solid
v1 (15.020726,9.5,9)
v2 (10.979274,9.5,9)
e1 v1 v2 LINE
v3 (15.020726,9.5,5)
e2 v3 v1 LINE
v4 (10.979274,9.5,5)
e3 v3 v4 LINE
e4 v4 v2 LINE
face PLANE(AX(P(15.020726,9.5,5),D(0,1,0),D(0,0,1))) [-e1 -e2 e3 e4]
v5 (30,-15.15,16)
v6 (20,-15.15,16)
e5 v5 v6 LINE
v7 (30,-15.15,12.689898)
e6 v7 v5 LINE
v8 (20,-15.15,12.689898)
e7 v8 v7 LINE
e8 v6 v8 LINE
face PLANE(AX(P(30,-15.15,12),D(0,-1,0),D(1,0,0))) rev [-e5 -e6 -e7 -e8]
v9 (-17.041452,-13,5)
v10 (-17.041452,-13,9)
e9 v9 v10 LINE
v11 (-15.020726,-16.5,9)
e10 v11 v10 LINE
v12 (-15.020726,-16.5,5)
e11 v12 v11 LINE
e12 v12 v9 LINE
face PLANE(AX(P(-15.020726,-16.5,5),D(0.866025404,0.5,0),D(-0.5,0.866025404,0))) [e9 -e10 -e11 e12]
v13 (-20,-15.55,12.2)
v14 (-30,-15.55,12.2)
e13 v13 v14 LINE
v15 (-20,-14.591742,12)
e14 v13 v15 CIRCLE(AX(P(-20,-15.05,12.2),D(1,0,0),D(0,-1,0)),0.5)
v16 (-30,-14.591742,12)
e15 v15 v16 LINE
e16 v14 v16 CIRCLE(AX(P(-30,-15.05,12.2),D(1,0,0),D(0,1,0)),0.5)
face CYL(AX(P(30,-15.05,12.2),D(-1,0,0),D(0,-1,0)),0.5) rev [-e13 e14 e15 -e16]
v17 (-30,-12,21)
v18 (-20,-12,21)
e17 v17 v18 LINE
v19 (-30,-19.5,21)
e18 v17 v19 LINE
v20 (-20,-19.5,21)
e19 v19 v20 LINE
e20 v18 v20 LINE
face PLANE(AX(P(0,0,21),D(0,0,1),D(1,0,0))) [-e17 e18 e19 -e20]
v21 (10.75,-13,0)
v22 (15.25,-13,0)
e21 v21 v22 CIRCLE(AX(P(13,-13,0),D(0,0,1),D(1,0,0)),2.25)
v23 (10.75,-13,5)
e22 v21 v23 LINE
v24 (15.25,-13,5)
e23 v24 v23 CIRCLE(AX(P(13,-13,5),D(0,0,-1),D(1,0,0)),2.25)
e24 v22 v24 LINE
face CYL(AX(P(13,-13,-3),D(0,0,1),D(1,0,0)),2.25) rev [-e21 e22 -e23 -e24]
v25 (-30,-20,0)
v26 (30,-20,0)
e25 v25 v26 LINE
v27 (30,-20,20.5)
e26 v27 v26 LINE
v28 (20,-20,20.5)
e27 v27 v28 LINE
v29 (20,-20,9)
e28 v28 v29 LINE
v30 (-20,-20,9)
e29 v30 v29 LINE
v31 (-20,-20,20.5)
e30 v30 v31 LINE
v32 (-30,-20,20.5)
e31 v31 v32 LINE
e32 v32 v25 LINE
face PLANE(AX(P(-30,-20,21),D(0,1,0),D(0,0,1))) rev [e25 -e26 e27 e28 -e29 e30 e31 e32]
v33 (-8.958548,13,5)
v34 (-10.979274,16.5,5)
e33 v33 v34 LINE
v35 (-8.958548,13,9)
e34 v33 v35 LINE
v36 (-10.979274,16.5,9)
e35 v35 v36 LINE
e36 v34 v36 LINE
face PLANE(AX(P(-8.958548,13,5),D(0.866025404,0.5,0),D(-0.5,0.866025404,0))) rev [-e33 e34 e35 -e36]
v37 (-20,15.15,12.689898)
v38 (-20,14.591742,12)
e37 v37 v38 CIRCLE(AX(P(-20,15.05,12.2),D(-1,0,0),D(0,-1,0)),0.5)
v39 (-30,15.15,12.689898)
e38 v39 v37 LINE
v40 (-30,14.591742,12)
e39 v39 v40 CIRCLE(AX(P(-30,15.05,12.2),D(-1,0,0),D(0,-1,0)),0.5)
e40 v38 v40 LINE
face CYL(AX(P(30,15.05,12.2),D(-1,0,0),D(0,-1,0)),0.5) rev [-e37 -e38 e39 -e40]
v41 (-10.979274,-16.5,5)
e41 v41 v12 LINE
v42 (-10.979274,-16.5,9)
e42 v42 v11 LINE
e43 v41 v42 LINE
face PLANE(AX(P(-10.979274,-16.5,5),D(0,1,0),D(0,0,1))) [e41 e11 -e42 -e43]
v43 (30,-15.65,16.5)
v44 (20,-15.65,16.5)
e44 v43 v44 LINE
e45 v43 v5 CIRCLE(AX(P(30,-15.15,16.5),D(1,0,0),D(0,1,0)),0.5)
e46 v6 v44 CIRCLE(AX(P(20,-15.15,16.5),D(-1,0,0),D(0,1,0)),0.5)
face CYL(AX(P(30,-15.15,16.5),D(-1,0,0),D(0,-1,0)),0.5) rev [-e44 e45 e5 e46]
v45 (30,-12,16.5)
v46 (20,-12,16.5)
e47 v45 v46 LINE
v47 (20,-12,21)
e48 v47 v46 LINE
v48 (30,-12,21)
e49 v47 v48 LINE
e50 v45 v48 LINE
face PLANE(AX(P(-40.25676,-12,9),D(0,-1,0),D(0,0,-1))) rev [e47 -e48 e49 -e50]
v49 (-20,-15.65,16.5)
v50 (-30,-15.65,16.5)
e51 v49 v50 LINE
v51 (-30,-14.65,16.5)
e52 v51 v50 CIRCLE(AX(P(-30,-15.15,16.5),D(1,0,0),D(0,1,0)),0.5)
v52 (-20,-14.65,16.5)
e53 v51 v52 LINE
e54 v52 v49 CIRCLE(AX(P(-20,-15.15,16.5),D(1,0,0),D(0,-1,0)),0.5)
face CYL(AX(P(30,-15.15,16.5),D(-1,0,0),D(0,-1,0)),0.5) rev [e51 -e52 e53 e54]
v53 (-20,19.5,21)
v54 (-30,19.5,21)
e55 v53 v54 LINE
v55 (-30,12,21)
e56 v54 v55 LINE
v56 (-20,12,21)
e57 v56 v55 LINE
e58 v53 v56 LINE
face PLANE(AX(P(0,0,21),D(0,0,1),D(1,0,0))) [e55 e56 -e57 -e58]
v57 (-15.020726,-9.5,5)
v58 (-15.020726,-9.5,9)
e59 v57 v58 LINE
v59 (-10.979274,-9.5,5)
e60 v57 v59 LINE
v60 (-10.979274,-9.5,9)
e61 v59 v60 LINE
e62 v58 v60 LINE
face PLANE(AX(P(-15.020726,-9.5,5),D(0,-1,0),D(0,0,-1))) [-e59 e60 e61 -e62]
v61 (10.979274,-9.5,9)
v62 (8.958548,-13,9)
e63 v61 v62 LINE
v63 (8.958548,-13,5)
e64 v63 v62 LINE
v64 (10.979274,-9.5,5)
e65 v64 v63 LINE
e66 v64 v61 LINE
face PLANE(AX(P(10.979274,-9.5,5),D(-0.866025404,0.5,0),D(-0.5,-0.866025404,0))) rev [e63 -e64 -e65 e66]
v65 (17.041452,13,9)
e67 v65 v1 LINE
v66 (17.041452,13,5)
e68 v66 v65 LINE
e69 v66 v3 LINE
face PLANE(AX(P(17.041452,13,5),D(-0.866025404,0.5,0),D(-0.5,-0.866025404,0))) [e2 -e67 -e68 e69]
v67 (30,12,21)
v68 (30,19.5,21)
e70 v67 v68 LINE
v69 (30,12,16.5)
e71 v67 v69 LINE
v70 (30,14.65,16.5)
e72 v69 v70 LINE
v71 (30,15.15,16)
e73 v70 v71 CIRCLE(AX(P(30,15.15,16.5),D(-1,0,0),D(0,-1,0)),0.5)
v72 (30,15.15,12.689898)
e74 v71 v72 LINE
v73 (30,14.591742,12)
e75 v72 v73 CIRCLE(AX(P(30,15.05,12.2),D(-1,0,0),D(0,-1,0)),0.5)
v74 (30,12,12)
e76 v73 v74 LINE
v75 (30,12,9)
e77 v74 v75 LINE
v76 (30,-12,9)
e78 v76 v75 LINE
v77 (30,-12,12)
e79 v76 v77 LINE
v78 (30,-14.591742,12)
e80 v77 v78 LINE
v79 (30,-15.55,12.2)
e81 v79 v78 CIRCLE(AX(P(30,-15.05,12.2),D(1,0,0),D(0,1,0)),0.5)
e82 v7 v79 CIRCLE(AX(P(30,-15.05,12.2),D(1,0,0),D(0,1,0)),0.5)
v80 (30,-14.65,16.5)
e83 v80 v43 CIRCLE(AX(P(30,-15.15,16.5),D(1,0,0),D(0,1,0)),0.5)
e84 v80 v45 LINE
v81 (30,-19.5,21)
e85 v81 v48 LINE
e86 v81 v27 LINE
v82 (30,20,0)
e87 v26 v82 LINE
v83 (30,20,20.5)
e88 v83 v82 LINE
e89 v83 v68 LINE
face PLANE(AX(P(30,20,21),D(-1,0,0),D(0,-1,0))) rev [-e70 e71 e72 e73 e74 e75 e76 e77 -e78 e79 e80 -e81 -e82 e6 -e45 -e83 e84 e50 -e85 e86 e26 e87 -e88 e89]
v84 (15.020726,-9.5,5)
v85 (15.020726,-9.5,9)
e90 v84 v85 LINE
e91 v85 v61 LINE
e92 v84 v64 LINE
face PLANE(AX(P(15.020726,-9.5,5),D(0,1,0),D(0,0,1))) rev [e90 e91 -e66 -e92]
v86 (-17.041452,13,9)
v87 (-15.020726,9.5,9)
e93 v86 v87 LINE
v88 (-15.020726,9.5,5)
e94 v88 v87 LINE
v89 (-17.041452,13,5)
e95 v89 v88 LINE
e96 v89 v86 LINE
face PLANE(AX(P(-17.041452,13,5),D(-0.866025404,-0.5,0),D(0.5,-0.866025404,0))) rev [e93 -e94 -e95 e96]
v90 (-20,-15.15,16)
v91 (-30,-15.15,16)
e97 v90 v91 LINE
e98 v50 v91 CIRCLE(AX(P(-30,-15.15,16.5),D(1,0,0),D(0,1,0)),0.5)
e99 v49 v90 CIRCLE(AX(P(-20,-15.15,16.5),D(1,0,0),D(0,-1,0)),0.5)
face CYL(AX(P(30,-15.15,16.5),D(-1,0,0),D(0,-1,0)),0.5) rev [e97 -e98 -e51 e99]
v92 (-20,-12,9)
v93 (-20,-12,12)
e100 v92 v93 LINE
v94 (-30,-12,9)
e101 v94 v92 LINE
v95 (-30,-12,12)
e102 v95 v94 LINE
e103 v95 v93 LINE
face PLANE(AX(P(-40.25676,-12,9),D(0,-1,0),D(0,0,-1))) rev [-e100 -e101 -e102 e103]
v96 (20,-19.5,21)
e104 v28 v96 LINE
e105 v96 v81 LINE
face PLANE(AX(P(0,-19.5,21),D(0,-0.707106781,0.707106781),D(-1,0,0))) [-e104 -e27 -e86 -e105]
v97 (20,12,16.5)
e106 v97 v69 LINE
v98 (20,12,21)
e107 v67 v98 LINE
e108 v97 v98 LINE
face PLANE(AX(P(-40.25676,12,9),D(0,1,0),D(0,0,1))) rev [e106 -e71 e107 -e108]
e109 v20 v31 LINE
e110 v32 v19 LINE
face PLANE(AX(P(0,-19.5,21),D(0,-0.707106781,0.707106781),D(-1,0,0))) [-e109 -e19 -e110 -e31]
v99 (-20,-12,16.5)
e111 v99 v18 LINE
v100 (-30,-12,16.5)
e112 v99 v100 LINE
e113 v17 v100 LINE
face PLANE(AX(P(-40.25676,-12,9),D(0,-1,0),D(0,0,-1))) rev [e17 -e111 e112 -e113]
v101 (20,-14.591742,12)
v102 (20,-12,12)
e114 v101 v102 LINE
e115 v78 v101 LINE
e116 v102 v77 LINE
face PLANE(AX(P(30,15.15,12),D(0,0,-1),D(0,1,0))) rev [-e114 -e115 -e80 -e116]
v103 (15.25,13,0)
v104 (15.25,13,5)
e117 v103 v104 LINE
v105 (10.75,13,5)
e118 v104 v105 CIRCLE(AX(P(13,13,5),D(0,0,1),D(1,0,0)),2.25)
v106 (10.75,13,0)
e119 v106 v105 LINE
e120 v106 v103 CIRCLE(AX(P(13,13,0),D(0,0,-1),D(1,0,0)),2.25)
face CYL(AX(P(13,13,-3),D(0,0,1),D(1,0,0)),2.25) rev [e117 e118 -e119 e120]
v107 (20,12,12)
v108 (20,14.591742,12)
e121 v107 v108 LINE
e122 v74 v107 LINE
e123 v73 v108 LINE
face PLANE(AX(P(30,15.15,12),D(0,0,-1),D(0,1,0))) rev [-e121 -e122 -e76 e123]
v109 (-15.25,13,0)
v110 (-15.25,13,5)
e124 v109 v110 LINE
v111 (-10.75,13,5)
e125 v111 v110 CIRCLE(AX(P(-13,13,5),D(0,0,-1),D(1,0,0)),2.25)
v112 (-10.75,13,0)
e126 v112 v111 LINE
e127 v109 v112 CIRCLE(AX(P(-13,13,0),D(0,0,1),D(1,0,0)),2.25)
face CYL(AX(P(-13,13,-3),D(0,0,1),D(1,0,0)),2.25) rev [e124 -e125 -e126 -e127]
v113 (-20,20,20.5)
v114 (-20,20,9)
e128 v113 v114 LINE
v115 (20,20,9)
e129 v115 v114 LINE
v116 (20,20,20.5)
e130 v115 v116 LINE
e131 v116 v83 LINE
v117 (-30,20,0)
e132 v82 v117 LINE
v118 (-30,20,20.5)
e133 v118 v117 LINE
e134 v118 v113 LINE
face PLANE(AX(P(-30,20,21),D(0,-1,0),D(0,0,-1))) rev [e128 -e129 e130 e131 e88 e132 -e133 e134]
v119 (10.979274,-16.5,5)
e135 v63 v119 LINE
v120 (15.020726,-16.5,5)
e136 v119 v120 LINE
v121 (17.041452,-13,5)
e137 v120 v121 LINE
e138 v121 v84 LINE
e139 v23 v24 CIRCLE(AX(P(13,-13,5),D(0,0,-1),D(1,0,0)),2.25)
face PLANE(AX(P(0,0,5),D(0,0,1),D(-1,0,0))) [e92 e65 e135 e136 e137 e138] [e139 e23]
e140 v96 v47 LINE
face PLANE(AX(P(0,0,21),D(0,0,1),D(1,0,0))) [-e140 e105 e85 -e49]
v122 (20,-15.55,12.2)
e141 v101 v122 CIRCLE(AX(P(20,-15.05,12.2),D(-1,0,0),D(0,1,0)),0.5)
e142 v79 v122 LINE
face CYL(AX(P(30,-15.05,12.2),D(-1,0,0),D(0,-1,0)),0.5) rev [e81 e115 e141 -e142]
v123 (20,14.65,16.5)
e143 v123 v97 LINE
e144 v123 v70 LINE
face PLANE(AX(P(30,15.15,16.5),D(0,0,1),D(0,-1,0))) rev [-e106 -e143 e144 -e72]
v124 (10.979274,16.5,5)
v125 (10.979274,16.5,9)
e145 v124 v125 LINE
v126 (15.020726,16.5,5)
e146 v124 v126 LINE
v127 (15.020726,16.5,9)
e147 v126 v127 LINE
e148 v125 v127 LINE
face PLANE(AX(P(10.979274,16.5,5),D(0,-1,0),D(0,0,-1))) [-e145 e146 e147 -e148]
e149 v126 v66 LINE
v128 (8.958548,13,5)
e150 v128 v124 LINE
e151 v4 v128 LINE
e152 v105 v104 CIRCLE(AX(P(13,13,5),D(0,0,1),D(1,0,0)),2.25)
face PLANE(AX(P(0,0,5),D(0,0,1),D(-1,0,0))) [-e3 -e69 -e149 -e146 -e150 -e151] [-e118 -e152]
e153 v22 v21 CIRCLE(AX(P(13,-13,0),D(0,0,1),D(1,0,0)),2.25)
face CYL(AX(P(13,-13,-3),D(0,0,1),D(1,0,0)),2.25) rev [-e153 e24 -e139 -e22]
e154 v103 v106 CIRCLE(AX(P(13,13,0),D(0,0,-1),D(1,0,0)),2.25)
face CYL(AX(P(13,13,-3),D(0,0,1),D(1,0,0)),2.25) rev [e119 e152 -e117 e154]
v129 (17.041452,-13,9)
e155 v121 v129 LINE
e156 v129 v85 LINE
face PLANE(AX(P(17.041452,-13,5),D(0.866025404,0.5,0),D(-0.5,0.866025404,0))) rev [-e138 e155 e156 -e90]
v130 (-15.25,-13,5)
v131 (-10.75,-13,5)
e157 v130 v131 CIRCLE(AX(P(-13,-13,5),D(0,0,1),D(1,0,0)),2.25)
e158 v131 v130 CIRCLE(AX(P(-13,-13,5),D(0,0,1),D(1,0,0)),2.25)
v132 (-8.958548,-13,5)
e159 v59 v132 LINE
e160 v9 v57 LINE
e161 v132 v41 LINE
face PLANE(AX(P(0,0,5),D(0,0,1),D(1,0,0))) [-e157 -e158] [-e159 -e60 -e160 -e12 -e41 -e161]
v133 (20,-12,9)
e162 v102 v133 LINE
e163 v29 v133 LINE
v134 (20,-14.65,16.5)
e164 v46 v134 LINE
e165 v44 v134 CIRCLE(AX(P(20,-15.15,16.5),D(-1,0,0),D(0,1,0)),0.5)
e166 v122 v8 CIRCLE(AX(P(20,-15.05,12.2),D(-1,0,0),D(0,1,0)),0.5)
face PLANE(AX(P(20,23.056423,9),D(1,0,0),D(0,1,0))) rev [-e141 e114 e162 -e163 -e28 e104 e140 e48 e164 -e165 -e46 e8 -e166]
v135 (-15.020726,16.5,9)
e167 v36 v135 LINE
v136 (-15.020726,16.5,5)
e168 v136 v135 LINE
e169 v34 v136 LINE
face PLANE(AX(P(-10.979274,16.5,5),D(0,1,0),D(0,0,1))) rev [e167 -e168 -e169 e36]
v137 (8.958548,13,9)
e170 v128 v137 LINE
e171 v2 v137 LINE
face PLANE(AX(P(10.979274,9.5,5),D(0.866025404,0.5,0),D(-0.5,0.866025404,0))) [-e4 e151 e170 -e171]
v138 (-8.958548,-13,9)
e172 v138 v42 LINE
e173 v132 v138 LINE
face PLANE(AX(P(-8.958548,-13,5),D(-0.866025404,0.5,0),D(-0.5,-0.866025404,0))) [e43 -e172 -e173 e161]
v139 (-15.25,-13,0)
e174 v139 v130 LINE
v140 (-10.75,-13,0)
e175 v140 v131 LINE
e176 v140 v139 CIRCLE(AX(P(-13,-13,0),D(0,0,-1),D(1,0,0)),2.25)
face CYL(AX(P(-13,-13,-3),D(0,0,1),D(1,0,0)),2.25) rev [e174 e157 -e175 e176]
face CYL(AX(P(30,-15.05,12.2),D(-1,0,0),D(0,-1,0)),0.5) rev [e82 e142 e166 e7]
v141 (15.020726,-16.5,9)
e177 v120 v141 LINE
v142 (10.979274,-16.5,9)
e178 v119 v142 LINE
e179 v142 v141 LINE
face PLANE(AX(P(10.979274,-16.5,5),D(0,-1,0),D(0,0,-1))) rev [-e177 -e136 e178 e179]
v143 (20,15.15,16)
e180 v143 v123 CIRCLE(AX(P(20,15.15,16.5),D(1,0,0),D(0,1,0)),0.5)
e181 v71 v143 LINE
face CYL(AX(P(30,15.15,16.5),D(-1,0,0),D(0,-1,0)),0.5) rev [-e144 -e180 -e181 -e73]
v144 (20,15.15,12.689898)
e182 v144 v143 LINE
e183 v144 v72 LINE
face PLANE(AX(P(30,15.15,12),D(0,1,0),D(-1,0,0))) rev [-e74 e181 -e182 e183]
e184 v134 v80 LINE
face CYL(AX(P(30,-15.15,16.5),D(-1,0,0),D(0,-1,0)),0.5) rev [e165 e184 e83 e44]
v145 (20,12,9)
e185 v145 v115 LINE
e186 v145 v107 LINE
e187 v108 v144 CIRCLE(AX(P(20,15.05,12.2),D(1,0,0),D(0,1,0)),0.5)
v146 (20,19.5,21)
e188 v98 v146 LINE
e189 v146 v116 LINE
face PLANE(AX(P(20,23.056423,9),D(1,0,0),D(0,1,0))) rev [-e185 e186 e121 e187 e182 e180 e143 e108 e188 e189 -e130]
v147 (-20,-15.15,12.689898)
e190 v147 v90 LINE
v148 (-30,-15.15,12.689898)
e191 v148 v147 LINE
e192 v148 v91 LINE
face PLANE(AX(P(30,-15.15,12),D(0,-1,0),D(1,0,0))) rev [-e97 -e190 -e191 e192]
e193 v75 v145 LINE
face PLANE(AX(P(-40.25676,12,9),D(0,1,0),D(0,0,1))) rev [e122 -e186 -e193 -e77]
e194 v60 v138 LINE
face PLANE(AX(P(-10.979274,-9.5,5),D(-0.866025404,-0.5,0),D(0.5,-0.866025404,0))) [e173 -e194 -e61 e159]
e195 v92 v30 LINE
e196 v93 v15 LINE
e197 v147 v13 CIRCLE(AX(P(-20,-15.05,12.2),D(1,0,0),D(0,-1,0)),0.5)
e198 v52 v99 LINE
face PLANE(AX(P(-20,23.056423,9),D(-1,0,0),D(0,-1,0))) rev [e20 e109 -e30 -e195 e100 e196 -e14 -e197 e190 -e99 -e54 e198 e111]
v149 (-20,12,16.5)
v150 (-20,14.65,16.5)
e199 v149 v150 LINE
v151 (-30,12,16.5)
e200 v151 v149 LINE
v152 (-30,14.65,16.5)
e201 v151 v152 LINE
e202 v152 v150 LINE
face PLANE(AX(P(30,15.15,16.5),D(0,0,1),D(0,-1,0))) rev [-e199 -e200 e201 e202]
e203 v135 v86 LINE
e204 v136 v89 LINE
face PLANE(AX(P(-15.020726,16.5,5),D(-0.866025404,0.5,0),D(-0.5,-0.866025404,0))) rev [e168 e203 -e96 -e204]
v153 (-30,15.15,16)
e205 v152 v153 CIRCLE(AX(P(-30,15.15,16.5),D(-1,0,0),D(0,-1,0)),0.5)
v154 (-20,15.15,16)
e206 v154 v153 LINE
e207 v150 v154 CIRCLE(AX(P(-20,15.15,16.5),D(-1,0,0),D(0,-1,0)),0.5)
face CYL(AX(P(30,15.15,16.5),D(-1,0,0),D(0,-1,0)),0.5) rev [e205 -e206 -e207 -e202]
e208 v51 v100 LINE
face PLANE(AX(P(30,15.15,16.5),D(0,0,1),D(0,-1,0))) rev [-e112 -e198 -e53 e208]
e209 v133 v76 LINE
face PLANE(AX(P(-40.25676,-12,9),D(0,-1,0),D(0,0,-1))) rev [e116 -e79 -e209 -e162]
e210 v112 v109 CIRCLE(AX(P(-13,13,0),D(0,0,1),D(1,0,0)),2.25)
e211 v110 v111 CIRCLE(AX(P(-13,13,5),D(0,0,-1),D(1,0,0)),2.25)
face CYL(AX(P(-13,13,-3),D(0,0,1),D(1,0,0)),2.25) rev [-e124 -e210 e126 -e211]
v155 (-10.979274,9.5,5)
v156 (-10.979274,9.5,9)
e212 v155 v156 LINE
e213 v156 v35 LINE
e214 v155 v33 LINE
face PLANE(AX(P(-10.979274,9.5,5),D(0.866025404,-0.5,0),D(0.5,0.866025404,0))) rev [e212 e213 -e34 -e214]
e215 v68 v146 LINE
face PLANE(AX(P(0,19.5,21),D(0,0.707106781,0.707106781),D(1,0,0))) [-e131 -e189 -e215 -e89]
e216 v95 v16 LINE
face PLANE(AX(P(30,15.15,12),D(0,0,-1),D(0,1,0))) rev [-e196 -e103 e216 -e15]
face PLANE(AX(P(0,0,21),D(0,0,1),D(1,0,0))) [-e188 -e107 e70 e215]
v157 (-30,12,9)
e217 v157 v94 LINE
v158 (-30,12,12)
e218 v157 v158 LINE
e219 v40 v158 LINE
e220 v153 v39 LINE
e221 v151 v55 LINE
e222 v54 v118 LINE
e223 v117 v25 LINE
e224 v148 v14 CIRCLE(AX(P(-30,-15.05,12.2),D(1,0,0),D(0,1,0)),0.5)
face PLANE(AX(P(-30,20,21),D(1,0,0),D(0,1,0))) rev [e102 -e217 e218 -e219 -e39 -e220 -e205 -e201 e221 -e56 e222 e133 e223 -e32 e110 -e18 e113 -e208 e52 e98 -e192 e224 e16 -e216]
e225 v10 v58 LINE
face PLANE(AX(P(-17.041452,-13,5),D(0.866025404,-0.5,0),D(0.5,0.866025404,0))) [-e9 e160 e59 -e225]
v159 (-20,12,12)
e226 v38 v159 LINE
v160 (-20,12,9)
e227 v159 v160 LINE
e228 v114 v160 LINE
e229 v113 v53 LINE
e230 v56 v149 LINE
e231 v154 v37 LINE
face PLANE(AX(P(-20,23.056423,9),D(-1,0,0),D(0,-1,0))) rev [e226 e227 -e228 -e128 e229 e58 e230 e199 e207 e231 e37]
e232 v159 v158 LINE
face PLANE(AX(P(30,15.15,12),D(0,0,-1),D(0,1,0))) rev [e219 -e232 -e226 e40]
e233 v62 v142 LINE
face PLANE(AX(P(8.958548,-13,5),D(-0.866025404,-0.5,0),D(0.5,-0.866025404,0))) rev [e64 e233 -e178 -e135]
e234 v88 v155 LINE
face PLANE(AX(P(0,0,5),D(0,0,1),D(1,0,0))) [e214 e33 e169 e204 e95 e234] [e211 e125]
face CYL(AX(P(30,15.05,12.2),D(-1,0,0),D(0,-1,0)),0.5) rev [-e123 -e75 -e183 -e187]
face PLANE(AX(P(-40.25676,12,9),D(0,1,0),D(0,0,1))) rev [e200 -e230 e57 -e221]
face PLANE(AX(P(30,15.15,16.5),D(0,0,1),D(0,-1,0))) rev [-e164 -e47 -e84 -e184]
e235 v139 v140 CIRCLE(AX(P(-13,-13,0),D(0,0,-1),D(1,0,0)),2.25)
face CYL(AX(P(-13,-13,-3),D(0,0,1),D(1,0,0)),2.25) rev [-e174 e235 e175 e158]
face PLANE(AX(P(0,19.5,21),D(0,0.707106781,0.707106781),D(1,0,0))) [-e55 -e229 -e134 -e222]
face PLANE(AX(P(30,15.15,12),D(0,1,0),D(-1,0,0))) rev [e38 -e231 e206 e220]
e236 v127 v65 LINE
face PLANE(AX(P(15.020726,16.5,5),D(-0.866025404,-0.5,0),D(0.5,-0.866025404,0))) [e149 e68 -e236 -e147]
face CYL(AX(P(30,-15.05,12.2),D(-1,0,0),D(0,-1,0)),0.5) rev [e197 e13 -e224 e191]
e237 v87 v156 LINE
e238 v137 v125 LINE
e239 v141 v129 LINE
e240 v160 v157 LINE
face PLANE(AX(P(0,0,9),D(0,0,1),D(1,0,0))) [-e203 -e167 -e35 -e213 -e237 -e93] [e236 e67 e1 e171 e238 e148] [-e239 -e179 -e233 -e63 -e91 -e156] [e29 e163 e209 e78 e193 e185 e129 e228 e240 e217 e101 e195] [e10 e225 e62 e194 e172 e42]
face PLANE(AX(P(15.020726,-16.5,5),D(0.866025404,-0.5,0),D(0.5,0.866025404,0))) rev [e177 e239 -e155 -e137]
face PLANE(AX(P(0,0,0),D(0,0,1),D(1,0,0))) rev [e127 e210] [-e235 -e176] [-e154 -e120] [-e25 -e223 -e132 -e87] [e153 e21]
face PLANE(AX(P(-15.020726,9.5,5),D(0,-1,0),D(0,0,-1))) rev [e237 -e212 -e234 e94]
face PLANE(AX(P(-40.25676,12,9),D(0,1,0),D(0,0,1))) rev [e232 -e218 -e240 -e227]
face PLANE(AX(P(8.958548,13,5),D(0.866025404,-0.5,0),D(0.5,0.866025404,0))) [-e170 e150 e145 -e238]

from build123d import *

# Parameters (mm, degrees)
SKETCH_1_W               = 60
SKETCH_1_H               = 40
EXTRUDE_1_DEPTH          = 21
SKETCH_2_W               = 40
SKETCH_2_H               = 46.112845628
CUT_EXTRUDE_1_DEPTH      = 12
SKETCH_3_W               = 80.513519028
SKETCH_3_H               = 24
CUT_EXTRUDE_2_DEPTH      = 12
SKETCH_4_W               = 4.5
SKETCH_4_H               = 30.3
CUT_EXTRUDE_3_DEPTH      = 67.640828326
SKETCH_5_R               = 2.25
CUT_EXTRUDE_4_DEPTH      = 12
MIRROR_2_COPY_1_SKETCH_R = 2.25
MIRROR_2_COPY_1_DEPTH    = 12
CUT_EXTRUDE_5_DEPTH      = 4
MIRROR_4_COPY_1_DEPTH    = 4
SKETCH_7_R               = 0.5
CUT_EXTRUDE_6_DEPTH      = 67.640828326
CHAMFER_1_SIZE           = 0.5


with BuildPart() as part:
    # 草图1 → 凸台-拉伸1 (new body)
    with BuildSketch(Plane.XY):
        Rectangle(SKETCH_1_W, SKETCH_1_H)
    extrude(amount=EXTRUDE_1_DEPTH)

    # 草图2 → 切除-拉伸1 (cut)
    with BuildSketch(Plane.XY.offset(21)):
        Rectangle(SKETCH_2_W, SKETCH_2_H)
    extrude(amount=-CUT_EXTRUDE_1_DEPTH, mode=Mode.SUBTRACT)

    # 草图3 → 切除-拉伸2 (cut)
    with BuildSketch(Plane.XY.offset(21)):
        Rectangle(SKETCH_3_W, SKETCH_3_H)
    extrude(amount=-CUT_EXTRUDE_2_DEPTH, mode=Mode.SUBTRACT)

    # 草图4 → 切除-拉伸3 (cut, through all)
    with BuildSketch(Plane.ZY.offset(30)):
        with Locations((14.25, 0)):
            Rectangle(SKETCH_4_W, SKETCH_4_H)
    extrude(amount=-CUT_EXTRUDE_3_DEPTH, mode=Mode.SUBTRACT)

    # 草图5 → 切除-拉伸4 (cut)
    with BuildSketch(Plane.XY.offset(9)):
        with Locations((-13, 13)):
            Circle(SKETCH_5_R)
    cut_extrude_4 = extrude(amount=-CUT_EXTRUDE_4_DEPTH, mode=Mode.SUBTRACT)

    # 镜向1: 切除-拉伸4 across plane
    add(cut_extrude_4.mirror(Plane.ZX), mode=Mode.SUBTRACT)

    # 镜向2: 切除-拉伸4 across plane
    add(cut_extrude_4.mirror(Plane(origin=(0, 0, 0), x_dir=(0, 0, 1), z_dir=(1, 0, 0))), mode=Mode.SUBTRACT)

    # 镜向2 copy 1 sketch → 镜向2 copy 1 (cut)
    with BuildSketch(Plane(origin=(0, 0, 9), x_dir=(-1, 0, 0), z_dir=(0, 0, 1))):
        with Locations((-13, 13)):
            Circle(MIRROR_2_COPY_1_SKETCH_R)
    extrude(amount=-MIRROR_2_COPY_1_DEPTH, mode=Mode.SUBTRACT)

    # 草图6 → 切除-拉伸5 (cut)
    with BuildSketch(Plane.XY.offset(9)):
        Polygon((-8.958548116, 13), (-10.979274058, 16.5), (-15.020725942, 16.5), (-17.041451884, 13), (-15.020725942, 9.5), (-10.979274058, 9.5), align=None)
    cut_extrude_5 = extrude(amount=-CUT_EXTRUDE_5_DEPTH, mode=Mode.SUBTRACT)

    # 镜向3: 切除-拉伸5 across plane
    add(cut_extrude_5.mirror(Plane(origin=(0, 0, 0), x_dir=(0, 0, 1), z_dir=(1, 0, 0))), mode=Mode.SUBTRACT)

    # 镜向4: 切除-拉伸5 across plane
    add(cut_extrude_5.mirror(Plane.ZX), mode=Mode.SUBTRACT)

    # 镜向4 copy 1 sketch → 镜向4 copy 1 (cut)
    with BuildSketch(Plane(origin=(0, 0, 9), x_dir=(-1, 0, 0), z_dir=(0, 0, 1))):
        Polygon((-8.958548116, 13), (-10.979274058, 16.5), (-15.020725942, 16.5), (-17.041451884, 13), (-15.020725942, 9.5), (-10.979274058, 9.5), align=None)
    extrude(amount=-MIRROR_4_COPY_1_DEPTH, mode=Mode.SUBTRACT)

    # 草图7 → 切除-拉伸6 (cut, through all)
    with BuildSketch(Plane.ZY.offset(30)):
        with Locations((12.2, 15.05)):
            Circle(SKETCH_7_R)
        with Locations((16.5, 15.15)):
            Circle(SKETCH_7_R)
    cut_extrude_6 = extrude(amount=-CUT_EXTRUDE_6_DEPTH, mode=Mode.SUBTRACT)

    # 镜向5: 切除-拉伸6 across plane
    add(cut_extrude_6.mirror(Plane.ZX), mode=Mode.SUBTRACT)

    # 倒角1
    chamfer_1_edges = [part.edges().sort_by_distance(p)[0] for p in [
        (-25, 20, 21),
        (25, -20, 21),
        (-25, -20, 21),
        (25, 20, 21),
    ]]
    chamfer(chamfer_1_edges, length=CHAMFER_1_SIZE)


solid = part.part
